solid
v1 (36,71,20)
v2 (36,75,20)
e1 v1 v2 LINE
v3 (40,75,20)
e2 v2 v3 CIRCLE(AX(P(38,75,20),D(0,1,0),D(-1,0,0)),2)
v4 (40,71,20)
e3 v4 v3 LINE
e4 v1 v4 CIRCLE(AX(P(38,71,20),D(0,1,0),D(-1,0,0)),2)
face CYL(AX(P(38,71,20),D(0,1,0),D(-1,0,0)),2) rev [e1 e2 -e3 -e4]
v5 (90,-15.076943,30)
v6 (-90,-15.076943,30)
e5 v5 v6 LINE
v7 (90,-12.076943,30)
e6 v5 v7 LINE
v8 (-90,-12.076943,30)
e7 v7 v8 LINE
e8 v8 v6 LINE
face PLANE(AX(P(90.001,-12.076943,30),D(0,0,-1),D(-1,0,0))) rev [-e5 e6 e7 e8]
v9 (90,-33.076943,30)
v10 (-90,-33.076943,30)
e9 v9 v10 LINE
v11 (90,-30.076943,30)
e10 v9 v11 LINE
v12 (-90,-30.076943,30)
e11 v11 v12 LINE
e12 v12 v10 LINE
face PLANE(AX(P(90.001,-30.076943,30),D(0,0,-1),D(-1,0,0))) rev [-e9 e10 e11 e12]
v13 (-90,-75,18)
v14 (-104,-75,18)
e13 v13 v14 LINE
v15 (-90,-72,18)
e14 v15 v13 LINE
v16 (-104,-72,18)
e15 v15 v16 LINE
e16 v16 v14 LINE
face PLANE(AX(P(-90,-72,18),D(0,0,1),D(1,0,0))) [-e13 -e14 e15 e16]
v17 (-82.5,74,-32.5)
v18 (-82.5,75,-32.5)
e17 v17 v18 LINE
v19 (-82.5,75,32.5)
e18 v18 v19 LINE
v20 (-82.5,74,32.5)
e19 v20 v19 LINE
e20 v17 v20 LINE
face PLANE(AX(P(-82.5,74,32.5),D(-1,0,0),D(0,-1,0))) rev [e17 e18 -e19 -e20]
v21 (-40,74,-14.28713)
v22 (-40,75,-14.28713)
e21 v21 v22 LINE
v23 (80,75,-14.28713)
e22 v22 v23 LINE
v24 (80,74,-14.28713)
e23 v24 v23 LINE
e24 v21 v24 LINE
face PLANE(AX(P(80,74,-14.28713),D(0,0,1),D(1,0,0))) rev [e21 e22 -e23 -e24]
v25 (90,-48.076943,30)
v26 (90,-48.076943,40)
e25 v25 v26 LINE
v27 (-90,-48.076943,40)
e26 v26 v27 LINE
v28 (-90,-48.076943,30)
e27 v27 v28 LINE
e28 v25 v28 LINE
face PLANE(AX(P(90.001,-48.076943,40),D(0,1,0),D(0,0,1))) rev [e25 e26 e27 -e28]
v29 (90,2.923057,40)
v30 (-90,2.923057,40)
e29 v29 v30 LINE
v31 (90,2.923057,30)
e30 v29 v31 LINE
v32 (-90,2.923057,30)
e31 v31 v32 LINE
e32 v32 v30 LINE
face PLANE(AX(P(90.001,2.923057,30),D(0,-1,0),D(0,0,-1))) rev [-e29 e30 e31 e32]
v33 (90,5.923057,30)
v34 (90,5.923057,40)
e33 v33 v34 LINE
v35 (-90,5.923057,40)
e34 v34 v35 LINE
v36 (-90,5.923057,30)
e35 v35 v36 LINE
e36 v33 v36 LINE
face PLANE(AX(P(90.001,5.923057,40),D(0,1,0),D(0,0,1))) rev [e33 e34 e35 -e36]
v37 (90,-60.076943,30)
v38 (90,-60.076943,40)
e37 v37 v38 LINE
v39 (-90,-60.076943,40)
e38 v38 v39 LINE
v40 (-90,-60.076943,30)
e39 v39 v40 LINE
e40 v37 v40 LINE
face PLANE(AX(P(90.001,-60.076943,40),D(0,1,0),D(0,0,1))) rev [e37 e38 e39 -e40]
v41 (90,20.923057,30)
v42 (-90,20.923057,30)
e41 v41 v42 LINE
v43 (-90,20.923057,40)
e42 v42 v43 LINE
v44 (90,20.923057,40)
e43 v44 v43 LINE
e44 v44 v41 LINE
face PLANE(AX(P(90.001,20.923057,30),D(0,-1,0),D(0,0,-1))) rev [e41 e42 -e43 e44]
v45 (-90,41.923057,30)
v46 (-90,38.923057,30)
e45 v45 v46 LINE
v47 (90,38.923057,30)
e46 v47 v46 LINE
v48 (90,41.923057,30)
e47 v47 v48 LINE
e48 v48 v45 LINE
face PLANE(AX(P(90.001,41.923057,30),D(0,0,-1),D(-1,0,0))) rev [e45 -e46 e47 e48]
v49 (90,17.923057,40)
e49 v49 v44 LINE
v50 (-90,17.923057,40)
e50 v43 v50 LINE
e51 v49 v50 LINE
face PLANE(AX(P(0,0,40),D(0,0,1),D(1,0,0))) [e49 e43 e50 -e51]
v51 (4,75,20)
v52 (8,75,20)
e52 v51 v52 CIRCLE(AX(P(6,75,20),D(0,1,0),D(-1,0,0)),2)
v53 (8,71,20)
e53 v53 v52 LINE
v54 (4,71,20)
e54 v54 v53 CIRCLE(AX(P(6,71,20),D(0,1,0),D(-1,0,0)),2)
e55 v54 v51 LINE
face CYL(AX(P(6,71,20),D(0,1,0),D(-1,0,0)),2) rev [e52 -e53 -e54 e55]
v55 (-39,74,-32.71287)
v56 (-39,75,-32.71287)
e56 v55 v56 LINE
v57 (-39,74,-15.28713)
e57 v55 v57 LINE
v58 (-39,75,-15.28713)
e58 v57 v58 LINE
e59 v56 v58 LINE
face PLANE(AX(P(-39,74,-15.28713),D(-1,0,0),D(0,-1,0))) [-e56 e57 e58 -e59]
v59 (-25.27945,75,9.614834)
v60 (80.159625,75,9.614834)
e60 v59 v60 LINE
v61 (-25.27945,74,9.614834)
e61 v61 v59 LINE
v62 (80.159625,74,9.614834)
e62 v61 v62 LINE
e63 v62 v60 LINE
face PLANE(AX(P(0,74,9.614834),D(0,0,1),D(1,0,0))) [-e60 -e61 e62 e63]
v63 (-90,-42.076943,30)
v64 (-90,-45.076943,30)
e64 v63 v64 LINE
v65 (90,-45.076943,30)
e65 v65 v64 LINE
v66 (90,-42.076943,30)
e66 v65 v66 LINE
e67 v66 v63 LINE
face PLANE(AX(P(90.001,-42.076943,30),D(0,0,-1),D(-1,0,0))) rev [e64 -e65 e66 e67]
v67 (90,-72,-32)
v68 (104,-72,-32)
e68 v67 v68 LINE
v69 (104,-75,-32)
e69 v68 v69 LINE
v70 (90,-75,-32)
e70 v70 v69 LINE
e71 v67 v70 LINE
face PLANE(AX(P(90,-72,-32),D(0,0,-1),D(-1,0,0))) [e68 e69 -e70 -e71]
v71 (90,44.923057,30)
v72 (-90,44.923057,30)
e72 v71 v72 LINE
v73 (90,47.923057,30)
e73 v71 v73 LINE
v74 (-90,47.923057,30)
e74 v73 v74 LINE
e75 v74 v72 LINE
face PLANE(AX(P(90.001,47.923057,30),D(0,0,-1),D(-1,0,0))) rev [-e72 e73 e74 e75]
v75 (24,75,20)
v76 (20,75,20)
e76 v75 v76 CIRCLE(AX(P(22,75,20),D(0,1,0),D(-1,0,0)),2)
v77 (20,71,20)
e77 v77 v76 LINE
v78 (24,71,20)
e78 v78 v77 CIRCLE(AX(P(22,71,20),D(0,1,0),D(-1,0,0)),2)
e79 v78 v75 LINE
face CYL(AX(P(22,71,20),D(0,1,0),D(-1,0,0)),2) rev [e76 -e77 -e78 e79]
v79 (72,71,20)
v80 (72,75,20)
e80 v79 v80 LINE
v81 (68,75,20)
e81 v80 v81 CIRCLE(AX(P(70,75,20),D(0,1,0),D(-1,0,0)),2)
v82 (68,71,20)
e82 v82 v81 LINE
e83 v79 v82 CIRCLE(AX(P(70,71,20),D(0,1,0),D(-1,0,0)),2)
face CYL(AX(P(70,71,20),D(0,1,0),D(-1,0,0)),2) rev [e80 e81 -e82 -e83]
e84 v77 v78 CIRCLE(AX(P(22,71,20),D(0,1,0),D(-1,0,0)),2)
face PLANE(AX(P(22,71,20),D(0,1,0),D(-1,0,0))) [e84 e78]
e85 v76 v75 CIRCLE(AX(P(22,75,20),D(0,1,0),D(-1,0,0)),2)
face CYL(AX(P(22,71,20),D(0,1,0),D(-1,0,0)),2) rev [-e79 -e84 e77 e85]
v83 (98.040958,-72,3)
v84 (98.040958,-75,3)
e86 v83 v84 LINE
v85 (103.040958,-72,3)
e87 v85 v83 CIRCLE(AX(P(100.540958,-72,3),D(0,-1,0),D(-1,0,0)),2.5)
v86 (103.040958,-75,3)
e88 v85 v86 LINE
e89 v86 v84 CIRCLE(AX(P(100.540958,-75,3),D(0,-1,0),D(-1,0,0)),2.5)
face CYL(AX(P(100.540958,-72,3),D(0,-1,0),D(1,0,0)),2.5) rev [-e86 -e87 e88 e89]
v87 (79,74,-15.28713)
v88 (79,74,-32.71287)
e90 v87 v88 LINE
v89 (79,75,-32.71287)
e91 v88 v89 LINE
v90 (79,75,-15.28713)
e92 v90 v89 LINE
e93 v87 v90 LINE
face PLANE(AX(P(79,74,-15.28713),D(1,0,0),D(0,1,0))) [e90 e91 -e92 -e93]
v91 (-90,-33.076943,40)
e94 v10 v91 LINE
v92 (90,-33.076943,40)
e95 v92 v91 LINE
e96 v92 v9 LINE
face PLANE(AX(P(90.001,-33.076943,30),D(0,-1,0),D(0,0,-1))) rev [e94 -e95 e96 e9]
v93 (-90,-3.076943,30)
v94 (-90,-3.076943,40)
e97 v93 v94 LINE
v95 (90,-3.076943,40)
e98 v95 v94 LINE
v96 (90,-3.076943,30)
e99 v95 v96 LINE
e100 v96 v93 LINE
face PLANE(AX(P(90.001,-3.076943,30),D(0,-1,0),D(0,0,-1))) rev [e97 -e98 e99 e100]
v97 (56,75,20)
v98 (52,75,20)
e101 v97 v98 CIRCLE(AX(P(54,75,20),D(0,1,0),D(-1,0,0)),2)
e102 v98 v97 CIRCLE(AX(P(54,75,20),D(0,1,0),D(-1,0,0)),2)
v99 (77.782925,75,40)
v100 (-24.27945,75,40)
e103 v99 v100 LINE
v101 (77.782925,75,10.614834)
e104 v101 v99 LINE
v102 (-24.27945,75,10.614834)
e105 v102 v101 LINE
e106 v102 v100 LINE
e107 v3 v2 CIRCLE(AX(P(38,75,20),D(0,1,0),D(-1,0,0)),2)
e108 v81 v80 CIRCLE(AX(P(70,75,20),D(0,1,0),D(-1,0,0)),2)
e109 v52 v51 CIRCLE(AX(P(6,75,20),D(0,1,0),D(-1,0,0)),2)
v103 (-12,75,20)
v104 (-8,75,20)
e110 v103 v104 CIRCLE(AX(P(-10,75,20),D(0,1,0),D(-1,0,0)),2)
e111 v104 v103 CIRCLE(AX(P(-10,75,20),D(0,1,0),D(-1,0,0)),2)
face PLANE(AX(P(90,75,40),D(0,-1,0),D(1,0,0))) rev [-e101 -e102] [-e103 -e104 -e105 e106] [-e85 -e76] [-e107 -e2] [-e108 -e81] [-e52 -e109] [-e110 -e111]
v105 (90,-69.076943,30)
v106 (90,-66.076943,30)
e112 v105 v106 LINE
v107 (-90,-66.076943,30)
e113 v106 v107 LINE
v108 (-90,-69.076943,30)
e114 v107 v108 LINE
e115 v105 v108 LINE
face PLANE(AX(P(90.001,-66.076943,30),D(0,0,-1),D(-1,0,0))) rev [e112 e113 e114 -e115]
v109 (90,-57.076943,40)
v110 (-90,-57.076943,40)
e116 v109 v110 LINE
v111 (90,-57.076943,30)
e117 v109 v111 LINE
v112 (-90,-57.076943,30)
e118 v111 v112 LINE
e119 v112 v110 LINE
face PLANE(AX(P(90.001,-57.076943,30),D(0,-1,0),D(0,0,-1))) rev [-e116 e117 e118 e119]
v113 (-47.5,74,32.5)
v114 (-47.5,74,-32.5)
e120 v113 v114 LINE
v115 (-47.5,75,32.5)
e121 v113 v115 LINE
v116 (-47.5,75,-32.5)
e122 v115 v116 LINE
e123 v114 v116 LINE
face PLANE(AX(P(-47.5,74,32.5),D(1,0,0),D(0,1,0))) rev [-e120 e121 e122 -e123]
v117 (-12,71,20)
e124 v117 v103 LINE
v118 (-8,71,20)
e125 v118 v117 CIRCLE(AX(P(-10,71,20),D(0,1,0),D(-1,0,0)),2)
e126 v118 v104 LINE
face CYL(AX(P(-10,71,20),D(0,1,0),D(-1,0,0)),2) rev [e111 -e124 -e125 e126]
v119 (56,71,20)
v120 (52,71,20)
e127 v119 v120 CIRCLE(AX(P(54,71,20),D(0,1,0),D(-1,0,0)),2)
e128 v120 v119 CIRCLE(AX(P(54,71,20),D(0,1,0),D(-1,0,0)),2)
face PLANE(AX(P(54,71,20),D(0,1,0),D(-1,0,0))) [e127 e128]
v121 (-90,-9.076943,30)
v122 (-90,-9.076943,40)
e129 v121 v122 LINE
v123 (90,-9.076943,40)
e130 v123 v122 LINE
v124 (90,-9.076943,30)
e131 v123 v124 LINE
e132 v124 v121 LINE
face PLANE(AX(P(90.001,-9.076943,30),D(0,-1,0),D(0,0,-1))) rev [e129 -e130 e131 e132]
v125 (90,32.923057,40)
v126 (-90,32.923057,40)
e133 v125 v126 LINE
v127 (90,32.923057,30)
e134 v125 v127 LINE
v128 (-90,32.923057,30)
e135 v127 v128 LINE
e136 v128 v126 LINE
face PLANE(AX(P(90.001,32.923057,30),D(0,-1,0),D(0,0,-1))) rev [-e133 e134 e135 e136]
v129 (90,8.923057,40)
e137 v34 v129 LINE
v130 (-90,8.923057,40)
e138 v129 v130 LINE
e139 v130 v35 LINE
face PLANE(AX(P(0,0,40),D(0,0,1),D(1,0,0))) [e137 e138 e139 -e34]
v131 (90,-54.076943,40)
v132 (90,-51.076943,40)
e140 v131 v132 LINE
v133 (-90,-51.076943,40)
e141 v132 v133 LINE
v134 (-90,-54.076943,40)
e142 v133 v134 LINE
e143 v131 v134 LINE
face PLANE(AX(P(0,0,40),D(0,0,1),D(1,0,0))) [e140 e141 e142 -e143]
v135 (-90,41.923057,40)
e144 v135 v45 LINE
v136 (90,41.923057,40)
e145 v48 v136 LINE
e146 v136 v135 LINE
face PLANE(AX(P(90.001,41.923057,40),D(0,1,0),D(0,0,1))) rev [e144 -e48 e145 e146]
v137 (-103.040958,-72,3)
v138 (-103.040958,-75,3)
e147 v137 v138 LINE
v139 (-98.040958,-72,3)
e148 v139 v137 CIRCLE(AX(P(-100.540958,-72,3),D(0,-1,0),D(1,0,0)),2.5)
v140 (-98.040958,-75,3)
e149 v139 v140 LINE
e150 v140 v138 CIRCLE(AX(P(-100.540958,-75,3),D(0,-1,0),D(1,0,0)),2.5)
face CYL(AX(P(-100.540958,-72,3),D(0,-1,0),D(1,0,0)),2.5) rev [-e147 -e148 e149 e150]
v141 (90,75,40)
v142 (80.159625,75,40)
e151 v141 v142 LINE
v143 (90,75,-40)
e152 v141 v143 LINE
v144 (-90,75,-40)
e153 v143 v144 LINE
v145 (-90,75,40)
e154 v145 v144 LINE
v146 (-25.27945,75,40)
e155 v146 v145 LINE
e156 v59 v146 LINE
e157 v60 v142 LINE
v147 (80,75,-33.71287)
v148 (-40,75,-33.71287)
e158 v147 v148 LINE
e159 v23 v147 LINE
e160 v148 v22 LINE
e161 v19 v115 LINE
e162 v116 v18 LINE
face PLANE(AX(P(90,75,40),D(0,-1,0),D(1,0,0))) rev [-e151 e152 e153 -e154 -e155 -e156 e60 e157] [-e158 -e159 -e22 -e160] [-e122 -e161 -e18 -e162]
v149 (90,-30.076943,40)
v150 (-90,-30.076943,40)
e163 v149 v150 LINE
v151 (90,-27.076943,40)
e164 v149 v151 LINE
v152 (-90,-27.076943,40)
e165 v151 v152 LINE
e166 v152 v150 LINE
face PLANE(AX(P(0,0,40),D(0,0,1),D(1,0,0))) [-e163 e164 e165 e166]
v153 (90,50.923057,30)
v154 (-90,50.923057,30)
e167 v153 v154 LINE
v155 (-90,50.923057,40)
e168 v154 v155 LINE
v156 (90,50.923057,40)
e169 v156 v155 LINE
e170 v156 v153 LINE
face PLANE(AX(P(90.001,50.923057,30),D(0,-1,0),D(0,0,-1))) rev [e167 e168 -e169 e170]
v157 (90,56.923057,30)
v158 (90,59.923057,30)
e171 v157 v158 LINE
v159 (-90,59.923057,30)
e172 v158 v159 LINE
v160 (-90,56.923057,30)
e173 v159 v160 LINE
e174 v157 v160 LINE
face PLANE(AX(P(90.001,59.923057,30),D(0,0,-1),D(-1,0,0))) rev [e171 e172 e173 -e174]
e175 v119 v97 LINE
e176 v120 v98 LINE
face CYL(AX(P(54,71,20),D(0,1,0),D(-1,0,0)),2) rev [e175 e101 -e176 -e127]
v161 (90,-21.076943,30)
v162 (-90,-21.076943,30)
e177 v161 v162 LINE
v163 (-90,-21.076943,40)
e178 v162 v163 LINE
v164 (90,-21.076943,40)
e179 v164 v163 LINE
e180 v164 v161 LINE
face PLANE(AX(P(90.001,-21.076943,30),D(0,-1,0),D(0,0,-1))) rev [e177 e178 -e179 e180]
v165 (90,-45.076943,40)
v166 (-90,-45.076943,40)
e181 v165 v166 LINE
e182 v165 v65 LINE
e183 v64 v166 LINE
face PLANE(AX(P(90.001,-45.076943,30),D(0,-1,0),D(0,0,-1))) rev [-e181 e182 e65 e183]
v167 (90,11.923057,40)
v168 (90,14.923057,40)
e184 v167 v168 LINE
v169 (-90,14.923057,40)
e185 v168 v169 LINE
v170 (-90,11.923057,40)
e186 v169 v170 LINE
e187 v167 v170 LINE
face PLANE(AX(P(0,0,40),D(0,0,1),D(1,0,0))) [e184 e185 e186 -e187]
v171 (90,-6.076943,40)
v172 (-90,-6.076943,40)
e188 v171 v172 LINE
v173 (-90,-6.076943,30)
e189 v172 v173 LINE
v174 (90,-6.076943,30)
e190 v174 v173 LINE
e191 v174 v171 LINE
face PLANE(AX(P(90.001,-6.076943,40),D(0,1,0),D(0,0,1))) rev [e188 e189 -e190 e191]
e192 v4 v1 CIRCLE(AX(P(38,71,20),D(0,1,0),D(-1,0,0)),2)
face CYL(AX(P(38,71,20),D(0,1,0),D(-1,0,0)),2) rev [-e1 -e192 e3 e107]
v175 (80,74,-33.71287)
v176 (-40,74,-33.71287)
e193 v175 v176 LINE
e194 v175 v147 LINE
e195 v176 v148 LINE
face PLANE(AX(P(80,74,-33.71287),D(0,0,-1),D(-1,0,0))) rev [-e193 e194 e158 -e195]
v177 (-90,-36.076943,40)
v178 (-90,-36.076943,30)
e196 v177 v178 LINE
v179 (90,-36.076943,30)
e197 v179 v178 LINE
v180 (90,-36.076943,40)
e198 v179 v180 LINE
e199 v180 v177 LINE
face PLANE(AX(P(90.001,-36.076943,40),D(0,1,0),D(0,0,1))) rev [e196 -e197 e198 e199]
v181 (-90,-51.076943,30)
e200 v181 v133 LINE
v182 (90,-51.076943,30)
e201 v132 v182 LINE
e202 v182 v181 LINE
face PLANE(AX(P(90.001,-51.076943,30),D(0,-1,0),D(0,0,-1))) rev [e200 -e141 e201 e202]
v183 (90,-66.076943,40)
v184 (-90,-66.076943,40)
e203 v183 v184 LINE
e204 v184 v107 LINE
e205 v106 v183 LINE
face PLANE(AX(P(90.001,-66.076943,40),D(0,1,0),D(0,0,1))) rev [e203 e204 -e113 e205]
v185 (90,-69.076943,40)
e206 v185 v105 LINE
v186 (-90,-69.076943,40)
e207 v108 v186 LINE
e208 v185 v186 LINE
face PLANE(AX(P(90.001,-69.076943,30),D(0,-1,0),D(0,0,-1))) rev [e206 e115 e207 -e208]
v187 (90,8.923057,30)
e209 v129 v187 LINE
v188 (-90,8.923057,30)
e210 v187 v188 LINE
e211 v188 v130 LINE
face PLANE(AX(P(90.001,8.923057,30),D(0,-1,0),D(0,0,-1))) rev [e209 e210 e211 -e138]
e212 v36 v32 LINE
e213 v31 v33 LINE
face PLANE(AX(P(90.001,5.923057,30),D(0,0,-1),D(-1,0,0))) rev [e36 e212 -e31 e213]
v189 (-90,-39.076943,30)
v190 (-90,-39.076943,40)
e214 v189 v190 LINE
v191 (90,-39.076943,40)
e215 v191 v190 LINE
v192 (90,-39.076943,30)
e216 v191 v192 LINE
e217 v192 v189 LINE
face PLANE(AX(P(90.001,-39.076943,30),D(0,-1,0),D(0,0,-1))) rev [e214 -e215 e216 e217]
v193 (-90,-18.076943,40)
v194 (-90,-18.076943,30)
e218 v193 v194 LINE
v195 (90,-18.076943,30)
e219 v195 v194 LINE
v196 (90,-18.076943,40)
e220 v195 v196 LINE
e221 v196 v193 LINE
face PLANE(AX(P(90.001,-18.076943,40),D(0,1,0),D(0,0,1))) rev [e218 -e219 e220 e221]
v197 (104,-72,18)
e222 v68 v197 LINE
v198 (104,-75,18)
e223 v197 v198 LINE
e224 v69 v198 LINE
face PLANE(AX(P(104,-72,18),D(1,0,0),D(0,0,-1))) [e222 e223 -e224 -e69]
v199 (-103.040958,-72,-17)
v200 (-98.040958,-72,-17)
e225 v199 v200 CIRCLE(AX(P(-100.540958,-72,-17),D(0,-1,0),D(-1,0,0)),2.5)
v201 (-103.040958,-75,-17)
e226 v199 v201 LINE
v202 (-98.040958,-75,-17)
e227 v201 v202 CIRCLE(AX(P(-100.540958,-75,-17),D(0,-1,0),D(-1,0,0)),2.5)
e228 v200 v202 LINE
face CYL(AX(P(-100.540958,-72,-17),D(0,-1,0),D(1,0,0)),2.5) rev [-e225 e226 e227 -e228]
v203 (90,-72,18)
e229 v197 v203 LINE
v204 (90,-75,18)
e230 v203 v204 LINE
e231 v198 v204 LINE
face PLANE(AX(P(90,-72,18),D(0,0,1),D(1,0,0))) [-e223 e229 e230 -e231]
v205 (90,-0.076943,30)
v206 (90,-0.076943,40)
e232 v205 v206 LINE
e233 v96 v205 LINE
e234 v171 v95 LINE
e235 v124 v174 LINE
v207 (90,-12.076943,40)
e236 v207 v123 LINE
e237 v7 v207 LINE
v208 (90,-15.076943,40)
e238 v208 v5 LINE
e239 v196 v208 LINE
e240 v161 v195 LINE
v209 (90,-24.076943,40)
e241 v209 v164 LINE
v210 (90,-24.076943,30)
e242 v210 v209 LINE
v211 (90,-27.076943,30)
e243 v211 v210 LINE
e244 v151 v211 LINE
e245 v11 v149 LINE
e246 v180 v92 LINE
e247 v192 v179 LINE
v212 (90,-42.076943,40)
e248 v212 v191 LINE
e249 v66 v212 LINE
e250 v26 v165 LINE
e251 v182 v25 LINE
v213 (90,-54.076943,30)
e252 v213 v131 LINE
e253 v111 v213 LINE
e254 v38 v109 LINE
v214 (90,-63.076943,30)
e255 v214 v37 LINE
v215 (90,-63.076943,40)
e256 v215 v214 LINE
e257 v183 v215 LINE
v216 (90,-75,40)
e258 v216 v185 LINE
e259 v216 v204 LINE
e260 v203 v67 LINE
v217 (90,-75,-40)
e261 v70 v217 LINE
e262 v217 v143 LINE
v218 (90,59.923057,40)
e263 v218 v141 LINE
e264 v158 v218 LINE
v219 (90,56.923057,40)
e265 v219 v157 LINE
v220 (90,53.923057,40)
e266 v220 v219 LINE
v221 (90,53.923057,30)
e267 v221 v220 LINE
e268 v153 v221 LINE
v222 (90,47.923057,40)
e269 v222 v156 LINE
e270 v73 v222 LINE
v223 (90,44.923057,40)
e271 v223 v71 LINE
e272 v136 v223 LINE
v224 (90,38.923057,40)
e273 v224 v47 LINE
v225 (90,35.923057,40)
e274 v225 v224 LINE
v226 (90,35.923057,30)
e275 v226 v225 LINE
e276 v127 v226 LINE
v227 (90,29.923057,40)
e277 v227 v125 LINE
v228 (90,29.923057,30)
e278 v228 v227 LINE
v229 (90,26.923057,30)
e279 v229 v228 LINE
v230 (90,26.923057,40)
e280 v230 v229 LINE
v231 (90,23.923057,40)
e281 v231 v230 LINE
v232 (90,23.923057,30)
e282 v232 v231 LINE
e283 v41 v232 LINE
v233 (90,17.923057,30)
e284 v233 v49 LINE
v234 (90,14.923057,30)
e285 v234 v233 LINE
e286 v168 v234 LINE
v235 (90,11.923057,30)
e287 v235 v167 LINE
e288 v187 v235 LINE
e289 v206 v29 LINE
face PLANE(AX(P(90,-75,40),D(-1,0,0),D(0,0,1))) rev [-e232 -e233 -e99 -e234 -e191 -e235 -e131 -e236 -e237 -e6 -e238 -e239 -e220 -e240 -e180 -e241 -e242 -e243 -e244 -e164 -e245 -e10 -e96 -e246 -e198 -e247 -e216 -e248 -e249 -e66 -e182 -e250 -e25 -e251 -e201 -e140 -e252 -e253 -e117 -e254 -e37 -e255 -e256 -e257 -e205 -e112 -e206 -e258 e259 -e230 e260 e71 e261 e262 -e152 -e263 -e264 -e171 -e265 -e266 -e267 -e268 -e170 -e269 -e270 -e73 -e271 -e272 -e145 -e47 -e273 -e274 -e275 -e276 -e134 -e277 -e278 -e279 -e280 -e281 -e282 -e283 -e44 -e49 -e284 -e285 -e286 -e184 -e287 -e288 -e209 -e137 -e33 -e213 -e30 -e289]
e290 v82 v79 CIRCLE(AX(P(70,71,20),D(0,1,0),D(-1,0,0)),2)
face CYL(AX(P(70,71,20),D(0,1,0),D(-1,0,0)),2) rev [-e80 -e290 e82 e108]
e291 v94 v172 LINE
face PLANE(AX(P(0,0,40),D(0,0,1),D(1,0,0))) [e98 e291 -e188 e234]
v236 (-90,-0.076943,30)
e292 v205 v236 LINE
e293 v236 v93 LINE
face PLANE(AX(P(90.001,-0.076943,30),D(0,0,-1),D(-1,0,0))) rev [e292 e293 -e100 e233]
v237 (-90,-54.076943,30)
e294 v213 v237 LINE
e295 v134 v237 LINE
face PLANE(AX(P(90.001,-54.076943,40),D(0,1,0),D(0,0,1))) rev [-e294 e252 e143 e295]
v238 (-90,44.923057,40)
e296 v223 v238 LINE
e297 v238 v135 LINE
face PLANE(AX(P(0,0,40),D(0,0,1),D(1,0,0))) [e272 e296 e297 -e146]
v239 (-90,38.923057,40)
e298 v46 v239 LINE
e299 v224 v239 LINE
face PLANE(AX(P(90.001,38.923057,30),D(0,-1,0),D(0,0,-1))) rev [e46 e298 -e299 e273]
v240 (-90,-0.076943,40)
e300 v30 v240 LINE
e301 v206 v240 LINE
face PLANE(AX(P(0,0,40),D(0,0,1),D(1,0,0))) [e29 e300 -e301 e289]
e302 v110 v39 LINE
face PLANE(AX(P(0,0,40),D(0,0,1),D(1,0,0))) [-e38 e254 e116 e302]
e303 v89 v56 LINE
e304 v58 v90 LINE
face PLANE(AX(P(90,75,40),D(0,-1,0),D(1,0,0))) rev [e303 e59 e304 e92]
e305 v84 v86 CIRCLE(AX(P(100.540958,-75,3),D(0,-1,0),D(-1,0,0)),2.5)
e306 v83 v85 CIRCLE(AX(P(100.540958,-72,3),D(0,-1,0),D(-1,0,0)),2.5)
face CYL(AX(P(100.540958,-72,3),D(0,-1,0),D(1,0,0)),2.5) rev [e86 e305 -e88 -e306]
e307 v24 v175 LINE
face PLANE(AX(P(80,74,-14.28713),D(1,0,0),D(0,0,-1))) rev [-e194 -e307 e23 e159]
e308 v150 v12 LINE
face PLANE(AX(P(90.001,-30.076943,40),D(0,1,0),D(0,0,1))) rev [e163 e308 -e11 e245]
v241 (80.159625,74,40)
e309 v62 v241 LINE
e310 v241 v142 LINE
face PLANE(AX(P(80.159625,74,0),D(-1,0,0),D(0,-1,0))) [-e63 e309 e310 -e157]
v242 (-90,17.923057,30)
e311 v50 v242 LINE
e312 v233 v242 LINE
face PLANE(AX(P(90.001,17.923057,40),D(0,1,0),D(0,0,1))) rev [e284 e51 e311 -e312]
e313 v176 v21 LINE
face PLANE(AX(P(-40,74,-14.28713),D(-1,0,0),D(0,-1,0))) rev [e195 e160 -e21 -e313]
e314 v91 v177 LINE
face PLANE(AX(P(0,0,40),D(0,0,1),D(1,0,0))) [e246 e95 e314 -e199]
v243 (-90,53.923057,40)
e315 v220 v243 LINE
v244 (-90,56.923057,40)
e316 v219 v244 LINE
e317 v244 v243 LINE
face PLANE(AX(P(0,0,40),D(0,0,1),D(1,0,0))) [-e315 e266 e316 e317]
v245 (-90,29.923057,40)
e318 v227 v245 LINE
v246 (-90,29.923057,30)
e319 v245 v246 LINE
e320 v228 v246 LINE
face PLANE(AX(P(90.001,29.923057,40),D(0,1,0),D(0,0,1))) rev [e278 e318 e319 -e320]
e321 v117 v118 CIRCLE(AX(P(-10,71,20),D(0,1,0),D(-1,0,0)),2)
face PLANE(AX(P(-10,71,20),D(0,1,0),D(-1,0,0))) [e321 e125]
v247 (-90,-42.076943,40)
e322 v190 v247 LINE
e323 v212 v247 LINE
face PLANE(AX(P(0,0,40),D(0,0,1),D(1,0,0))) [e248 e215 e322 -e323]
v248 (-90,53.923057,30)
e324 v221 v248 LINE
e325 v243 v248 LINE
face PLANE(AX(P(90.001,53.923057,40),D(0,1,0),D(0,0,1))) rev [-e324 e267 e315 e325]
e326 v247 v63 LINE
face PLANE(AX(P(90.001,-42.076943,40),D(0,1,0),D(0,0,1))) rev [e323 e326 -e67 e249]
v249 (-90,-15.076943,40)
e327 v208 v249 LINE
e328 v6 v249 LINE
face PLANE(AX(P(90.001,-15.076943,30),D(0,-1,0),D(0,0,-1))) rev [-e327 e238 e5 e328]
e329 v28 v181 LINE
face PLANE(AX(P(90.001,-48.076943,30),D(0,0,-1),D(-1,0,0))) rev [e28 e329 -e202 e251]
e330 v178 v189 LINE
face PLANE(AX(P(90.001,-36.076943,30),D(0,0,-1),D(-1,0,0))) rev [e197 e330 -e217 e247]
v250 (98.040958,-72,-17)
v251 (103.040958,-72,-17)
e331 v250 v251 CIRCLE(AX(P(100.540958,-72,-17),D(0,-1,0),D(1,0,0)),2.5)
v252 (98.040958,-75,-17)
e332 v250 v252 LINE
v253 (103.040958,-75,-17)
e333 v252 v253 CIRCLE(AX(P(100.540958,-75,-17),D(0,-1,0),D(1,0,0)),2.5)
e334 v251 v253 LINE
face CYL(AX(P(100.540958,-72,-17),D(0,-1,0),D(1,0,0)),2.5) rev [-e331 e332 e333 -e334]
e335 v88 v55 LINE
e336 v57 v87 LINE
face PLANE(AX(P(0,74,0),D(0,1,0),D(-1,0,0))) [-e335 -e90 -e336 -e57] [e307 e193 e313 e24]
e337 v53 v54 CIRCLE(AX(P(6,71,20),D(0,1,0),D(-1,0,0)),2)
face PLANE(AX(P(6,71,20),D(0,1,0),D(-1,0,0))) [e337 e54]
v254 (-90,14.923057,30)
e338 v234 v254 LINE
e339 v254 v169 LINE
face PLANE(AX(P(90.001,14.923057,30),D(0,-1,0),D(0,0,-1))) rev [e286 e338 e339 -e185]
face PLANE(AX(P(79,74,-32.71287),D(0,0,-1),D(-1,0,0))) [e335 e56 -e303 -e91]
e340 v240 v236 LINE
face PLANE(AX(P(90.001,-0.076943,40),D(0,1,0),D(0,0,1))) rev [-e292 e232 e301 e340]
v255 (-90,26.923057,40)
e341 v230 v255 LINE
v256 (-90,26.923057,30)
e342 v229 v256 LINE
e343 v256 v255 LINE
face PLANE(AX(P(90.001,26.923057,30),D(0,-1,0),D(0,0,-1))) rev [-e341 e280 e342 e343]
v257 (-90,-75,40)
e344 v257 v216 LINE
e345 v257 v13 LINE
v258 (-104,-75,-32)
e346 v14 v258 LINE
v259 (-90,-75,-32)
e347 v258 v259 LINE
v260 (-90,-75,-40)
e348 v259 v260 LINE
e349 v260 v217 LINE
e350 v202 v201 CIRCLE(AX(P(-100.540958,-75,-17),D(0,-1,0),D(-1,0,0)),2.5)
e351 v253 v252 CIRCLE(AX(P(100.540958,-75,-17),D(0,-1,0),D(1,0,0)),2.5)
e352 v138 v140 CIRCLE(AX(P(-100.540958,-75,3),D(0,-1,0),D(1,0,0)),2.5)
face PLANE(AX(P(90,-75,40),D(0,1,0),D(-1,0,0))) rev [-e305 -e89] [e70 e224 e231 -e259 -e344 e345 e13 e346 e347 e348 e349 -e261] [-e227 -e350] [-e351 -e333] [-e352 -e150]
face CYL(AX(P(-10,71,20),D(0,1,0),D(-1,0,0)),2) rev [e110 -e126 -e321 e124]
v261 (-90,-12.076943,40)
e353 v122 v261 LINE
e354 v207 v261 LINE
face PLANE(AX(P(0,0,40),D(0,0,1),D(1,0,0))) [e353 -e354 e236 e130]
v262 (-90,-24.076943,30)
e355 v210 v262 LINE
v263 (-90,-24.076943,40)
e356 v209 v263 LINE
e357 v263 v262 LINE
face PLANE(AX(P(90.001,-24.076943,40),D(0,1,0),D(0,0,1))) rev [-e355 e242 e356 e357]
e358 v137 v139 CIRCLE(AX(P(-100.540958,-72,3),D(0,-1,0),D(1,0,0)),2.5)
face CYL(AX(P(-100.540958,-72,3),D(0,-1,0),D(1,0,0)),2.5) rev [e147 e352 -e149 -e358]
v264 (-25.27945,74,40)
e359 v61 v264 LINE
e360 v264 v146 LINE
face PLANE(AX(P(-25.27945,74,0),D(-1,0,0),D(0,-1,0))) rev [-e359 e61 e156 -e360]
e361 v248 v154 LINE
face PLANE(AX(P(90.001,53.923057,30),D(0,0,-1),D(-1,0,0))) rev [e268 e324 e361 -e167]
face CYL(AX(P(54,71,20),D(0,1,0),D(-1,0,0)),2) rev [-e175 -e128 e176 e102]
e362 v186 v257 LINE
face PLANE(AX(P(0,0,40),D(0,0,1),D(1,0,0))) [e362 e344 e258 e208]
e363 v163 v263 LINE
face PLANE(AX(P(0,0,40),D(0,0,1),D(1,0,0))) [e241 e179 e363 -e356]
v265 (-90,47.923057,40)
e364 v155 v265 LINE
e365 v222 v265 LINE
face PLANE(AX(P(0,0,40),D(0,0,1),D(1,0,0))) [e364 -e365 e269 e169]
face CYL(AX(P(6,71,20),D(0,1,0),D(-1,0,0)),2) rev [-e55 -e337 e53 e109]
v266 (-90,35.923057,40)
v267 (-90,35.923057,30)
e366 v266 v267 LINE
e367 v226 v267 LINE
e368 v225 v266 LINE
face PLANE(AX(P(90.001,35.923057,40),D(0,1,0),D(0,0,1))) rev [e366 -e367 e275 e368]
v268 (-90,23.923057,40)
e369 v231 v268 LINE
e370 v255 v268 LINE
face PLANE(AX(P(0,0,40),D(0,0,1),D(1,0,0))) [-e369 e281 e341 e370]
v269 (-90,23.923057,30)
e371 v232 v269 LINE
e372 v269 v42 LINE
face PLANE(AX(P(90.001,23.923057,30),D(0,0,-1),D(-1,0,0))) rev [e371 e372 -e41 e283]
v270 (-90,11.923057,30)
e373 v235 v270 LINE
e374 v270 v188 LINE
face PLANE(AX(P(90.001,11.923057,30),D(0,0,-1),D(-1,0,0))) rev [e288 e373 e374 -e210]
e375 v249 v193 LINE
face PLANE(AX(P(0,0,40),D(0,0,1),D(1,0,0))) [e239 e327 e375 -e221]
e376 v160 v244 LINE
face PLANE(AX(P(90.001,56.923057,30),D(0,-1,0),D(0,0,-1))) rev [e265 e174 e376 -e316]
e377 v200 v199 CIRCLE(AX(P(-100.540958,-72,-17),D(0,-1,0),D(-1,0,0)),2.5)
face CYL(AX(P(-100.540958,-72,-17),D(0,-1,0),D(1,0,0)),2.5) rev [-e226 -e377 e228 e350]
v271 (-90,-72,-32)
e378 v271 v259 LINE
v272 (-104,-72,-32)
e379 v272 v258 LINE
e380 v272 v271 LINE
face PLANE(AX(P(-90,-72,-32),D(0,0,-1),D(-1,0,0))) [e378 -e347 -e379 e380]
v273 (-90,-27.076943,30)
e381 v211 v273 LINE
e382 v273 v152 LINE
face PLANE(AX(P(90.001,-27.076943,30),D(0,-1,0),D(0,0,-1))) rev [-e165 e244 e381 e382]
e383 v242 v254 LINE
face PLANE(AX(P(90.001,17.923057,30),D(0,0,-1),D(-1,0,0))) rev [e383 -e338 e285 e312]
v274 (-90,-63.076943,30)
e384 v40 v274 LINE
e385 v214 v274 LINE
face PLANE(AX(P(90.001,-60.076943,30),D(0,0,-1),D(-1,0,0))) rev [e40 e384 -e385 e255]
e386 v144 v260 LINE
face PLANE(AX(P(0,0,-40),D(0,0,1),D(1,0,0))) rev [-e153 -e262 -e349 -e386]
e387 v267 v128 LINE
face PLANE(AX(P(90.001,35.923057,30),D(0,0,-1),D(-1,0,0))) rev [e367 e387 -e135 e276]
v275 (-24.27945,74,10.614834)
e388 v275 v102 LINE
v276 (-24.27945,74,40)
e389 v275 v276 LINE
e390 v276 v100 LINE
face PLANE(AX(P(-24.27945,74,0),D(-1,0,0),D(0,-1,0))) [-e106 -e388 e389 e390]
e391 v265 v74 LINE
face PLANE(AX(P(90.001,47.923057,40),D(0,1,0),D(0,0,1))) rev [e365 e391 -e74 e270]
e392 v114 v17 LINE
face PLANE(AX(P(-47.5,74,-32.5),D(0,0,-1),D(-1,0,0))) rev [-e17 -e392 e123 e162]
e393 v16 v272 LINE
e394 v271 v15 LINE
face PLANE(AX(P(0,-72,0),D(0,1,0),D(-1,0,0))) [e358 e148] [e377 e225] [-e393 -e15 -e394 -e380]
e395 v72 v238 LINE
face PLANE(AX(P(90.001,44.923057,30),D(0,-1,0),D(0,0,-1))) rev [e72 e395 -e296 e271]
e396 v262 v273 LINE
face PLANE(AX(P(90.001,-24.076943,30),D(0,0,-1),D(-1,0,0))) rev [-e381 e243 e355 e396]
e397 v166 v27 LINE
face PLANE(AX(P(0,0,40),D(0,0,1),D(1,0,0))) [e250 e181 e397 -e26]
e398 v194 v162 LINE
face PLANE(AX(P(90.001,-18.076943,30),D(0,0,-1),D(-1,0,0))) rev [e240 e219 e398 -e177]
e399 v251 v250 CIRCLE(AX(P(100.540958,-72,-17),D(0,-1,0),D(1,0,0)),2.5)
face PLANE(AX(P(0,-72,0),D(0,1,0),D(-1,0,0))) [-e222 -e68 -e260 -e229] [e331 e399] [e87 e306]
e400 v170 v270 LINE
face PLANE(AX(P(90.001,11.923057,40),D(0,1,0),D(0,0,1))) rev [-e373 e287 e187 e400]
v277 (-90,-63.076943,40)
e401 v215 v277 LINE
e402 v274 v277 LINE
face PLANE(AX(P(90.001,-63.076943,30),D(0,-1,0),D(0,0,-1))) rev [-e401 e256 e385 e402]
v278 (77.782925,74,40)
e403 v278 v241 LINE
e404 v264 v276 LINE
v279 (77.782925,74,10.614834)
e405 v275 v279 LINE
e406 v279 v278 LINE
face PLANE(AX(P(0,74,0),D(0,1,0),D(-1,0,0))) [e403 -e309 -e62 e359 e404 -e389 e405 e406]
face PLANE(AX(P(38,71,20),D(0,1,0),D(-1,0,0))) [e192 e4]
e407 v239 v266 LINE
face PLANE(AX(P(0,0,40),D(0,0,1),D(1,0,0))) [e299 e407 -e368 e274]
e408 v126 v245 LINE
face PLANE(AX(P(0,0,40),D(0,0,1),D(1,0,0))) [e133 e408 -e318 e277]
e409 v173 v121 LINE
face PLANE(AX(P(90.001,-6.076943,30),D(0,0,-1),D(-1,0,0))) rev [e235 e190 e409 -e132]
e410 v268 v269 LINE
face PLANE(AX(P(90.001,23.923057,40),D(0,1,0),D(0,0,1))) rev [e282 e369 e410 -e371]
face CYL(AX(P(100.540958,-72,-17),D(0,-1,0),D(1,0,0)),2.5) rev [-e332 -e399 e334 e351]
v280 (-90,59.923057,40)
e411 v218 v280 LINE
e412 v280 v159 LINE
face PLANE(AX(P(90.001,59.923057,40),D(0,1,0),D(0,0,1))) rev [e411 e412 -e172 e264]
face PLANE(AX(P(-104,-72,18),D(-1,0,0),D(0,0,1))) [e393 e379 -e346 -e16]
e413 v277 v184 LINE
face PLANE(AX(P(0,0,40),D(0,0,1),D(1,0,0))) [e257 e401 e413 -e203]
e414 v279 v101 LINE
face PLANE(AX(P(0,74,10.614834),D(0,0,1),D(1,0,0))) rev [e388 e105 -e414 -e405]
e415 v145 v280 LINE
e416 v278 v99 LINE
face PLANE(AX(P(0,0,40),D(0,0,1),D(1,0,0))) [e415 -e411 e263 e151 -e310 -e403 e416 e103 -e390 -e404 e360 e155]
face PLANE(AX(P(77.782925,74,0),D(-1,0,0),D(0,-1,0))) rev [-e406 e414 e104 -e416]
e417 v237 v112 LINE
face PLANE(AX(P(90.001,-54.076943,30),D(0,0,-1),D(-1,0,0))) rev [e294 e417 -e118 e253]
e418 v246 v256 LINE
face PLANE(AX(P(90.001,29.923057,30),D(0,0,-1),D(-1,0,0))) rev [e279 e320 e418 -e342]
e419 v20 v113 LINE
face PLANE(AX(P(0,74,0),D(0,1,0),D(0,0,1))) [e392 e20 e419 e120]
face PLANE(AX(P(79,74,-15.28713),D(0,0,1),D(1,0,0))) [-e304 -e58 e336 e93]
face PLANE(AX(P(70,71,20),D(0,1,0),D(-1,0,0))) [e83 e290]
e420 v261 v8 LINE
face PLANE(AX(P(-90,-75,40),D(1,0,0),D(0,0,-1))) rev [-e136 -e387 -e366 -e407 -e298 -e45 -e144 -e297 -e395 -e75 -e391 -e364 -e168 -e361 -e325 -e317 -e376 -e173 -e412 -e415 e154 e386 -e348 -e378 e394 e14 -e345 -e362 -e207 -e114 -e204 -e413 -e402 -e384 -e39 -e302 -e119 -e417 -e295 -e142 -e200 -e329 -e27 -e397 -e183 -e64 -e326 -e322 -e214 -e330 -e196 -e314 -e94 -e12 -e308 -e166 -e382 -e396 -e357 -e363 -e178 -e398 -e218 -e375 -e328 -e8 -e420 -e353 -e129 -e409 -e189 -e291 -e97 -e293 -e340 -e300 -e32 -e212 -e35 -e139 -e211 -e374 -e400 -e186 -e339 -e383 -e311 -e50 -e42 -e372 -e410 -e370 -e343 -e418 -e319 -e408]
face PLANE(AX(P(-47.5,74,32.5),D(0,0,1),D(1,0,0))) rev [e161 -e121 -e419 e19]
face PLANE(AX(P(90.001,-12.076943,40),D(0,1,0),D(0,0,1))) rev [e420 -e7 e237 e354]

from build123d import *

# Parameters (mm, degrees)
SKETCH_1_W          = 180
SKETCH_1_H          = 150
EXTRUDE_1_DEPTH     = 40
CUT_EXTRUDE_1_REACH = 201.06
SKETCH_2_W          = 10
SKETCH_2_H          = 3
SKETCH_3_W          = 35
SKETCH_3_H          = 65
CUT_EXTRUDE_2_DEPTH = 1
SKETCH_4_W          = 120
SKETCH_4_H          = 19.42574098
SKETCH_4_W_2        = 118
SKETCH_4_H_2        = 17.42574098
CUT_EXTRUDE_3_DEPTH = 1
SKETCH_5_W          = 14
SKETCH_5_H          = 50
SKETCH_5_R          = 2.5
EXTRUDE_2_DEPTH     = 3
SKETCH_6_R          = 2
CUT_EXTRUDE_4_DEPTH = 4
CUT_EXTRUDE_5_DEPTH = 1


with BuildPart() as part:
    # 草图1 → 凸台-拉伸1 (new, symmetric)
    with BuildSketch(Plane.XY):
        Rectangle(SKETCH_1_W, SKETCH_1_H)
    extrude(amount=EXTRUDE_1_DEPTH, both=True)

    # 草图2 → 切除-拉伸1 (cut, up to next)
    with BuildSketch(Plane.ZY.offset(90), mode=Mode.PRIVATE) as cut_extrude_1_sk1:
        with Locations((35, 58.423056781)):
            Rectangle(SKETCH_2_W, SKETCH_2_H)
    cut_extrude_1_tool1 = extrude(cut_extrude_1_sk1.sketch, amount=-CUT_EXTRUDE_1_REACH, mode=Mode.PRIVATE) & part.part
    # 草图2 → 切除-拉伸1 (cut, up to next)
    with BuildSketch(Plane.ZY.offset(90), mode=Mode.PRIVATE) as cut_extrude_1_sk2:
        with Locations((35, 52.423056781)):
            Rectangle(SKETCH_2_W, SKETCH_2_H)
    cut_extrude_1_tool2 = extrude(cut_extrude_1_sk2.sketch, amount=-CUT_EXTRUDE_1_REACH, mode=Mode.PRIVATE) & part.part
    # 草图2 → 切除-拉伸1 (cut, up to next)
    with BuildSketch(Plane.ZY.offset(90), mode=Mode.PRIVATE) as cut_extrude_1_sk3:
        with Locations((35, 46.423056781)):
            Rectangle(SKETCH_2_W, SKETCH_2_H)
    cut_extrude_1_tool3 = extrude(cut_extrude_1_sk3.sketch, amount=-CUT_EXTRUDE_1_REACH, mode=Mode.PRIVATE) & part.part
    # 草图2 → 切除-拉伸1 (cut, up to next)
    with BuildSketch(Plane.ZY.offset(90), mode=Mode.PRIVATE) as cut_extrude_1_sk4:
        with Locations((35, 40.423056781)):
            Rectangle(SKETCH_2_W, SKETCH_2_H)
    cut_extrude_1_tool4 = extrude(cut_extrude_1_sk4.sketch, amount=-CUT_EXTRUDE_1_REACH, mode=Mode.PRIVATE) & part.part
    # 草图2 → 切除-拉伸1 (cut, up to next)
    with BuildSketch(Plane.ZY.offset(90), mode=Mode.PRIVATE) as cut_extrude_1_sk5:
        with Locations((35, 34.423056781)):
            Rectangle(SKETCH_2_W, SKETCH_2_H)
    cut_extrude_1_tool5 = extrude(cut_extrude_1_sk5.sketch, amount=-CUT_EXTRUDE_1_REACH, mode=Mode.PRIVATE) & part.part
    # 草图2 → 切除-拉伸1 (cut, up to next)
    with BuildSketch(Plane.ZY.offset(90), mode=Mode.PRIVATE) as cut_extrude_1_sk6:
        with Locations((35, 28.423056781)):
            Rectangle(SKETCH_2_W, SKETCH_2_H)
    cut_extrude_1_tool6 = extrude(cut_extrude_1_sk6.sketch, amount=-CUT_EXTRUDE_1_REACH, mode=Mode.PRIVATE) & part.part
    # 草图2 → 切除-拉伸1 (cut, up to next)
    with BuildSketch(Plane.ZY.offset(90), mode=Mode.PRIVATE) as cut_extrude_1_sk7:
        with Locations((35, 22.423056781)):
            Rectangle(SKETCH_2_W, SKETCH_2_H)
    cut_extrude_1_tool7 = extrude(cut_extrude_1_sk7.sketch, amount=-CUT_EXTRUDE_1_REACH, mode=Mode.PRIVATE) & part.part
    # 草图2 → 切除-拉伸1 (cut, up to next)
    with BuildSketch(Plane.ZY.offset(90), mode=Mode.PRIVATE) as cut_extrude_1_sk8:
        with Locations((35, 16.423056781)):
            Rectangle(SKETCH_2_W, SKETCH_2_H)
    cut_extrude_1_tool8 = extrude(cut_extrude_1_sk8.sketch, amount=-CUT_EXTRUDE_1_REACH, mode=Mode.PRIVATE) & part.part
    # 草图2 → 切除-拉伸1 (cut, up to next)
    with BuildSketch(Plane.ZY.offset(90), mode=Mode.PRIVATE) as cut_extrude_1_sk9:
        with Locations((35, 10.423056781)):
            Rectangle(SKETCH_2_W, SKETCH_2_H)
    cut_extrude_1_tool9 = extrude(cut_extrude_1_sk9.sketch, amount=-CUT_EXTRUDE_1_REACH, mode=Mode.PRIVATE) & part.part
    # 草图2 → 切除-拉伸1 (cut, up to next)
    with BuildSketch(Plane.ZY.offset(90), mode=Mode.PRIVATE) as cut_extrude_1_sk10:
        with Locations((35, 4.423056781)):
            Rectangle(SKETCH_2_W, SKETCH_2_H)
    cut_extrude_1_tool10 = extrude(cut_extrude_1_sk10.sketch, amount=-CUT_EXTRUDE_1_REACH, mode=Mode.PRIVATE) & part.part
    # 草图2 → 切除-拉伸1 (cut, up to next)
    with BuildSketch(Plane.ZY.offset(90), mode=Mode.PRIVATE) as cut_extrude_1_sk11:
        with Locations((35, -1.576943219)):
            Rectangle(SKETCH_2_W, SKETCH_2_H)
    cut_extrude_1_tool11 = extrude(cut_extrude_1_sk11.sketch, amount=-CUT_EXTRUDE_1_REACH, mode=Mode.PRIVATE) & part.part
    # 草图2 → 切除-拉伸1 (cut, up to next)
    with BuildSketch(Plane.ZY.offset(90), mode=Mode.PRIVATE) as cut_extrude_1_sk12:
        with Locations((35, -7.576943219)):
            Rectangle(SKETCH_2_W, SKETCH_2_H)
    cut_extrude_1_tool12 = extrude(cut_extrude_1_sk12.sketch, amount=-CUT_EXTRUDE_1_REACH, mode=Mode.PRIVATE) & part.part
    # 草图2 → 切除-拉伸1 (cut, up to next)
    with BuildSketch(Plane.ZY.offset(90), mode=Mode.PRIVATE) as cut_extrude_1_sk13:
        with Locations((35, -13.576943219)):
            Rectangle(SKETCH_2_W, SKETCH_2_H)
    cut_extrude_1_tool13 = extrude(cut_extrude_1_sk13.sketch, amount=-CUT_EXTRUDE_1_REACH, mode=Mode.PRIVATE) & part.part
    # 草图2 → 切除-拉伸1 (cut, up to next)
    with BuildSketch(Plane.ZY.offset(90), mode=Mode.PRIVATE) as cut_extrude_1_sk14:
        with Locations((35, -19.576943219)):
            Rectangle(SKETCH_2_W, SKETCH_2_H)
    cut_extrude_1_tool14 = extrude(cut_extrude_1_sk14.sketch, amount=-CUT_EXTRUDE_1_REACH, mode=Mode.PRIVATE) & part.part
    # 草图2 → 切除-拉伸1 (cut, up to next)
    with BuildSketch(Plane.ZY.offset(90), mode=Mode.PRIVATE) as cut_extrude_1_sk15:
        with Locations((35, -25.576943219)):
            Rectangle(SKETCH_2_W, SKETCH_2_H)
    cut_extrude_1_tool15 = extrude(cut_extrude_1_sk15.sketch, amount=-CUT_EXTRUDE_1_REACH, mode=Mode.PRIVATE) & part.part
    # 草图2 → 切除-拉伸1 (cut, up to next)
    with BuildSketch(Plane.ZY.offset(90), mode=Mode.PRIVATE) as cut_extrude_1_sk16:
        with Locations((35, -31.576943219)):
            Rectangle(SKETCH_2_W, SKETCH_2_H)
    cut_extrude_1_tool16 = extrude(cut_extrude_1_sk16.sketch, amount=-CUT_EXTRUDE_1_REACH, mode=Mode.PRIVATE) & part.part
    # 草图2 → 切除-拉伸1 (cut, up to next)
    with BuildSketch(Plane.ZY.offset(90), mode=Mode.PRIVATE) as cut_extrude_1_sk17:
        with Locations((35, -37.576943219)):
            Rectangle(SKETCH_2_W, SKETCH_2_H)
    cut_extrude_1_tool17 = extrude(cut_extrude_1_sk17.sketch, amount=-CUT_EXTRUDE_1_REACH, mode=Mode.PRIVATE) & part.part
    # 草图2 → 切除-拉伸1 (cut, up to next)
    with BuildSketch(Plane.ZY.offset(90), mode=Mode.PRIVATE) as cut_extrude_1_sk18:
        with Locations((35, -43.576943219)):
            Rectangle(SKETCH_2_W, SKETCH_2_H)
    cut_extrude_1_tool18 = extrude(cut_extrude_1_sk18.sketch, amount=-CUT_EXTRUDE_1_REACH, mode=Mode.PRIVATE) & part.part
    # 草图2 → 切除-拉伸1 (cut, up to next)
    with BuildSketch(Plane.ZY.offset(90), mode=Mode.PRIVATE) as cut_extrude_1_sk19:
        with Locations((35, -49.576943219)):
            Rectangle(SKETCH_2_W, SKETCH_2_H)
    cut_extrude_1_tool19 = extrude(cut_extrude_1_sk19.sketch, amount=-CUT_EXTRUDE_1_REACH, mode=Mode.PRIVATE) & part.part
    # 草图2 → 切除-拉伸1 (cut, up to next)
    with BuildSketch(Plane.ZY.offset(90), mode=Mode.PRIVATE) as cut_extrude_1_sk20:
        with Locations((35, -55.576943219)):
            Rectangle(SKETCH_2_W, SKETCH_2_H)
    cut_extrude_1_tool20 = extrude(cut_extrude_1_sk20.sketch, amount=-CUT_EXTRUDE_1_REACH, mode=Mode.PRIVATE) & part.part
    # 草图2 → 切除-拉伸1 (cut, up to next)
    with BuildSketch(Plane.ZY.offset(90), mode=Mode.PRIVATE) as cut_extrude_1_sk21:
        with Locations((35, -61.576943219)):
            Rectangle(SKETCH_2_W, SKETCH_2_H)
    cut_extrude_1_tool21 = extrude(cut_extrude_1_sk21.sketch, amount=-CUT_EXTRUDE_1_REACH, mode=Mode.PRIVATE) & part.part
    # 草图2 → 切除-拉伸1 (cut, up to next)
    with BuildSketch(Plane.ZY.offset(90), mode=Mode.PRIVATE) as cut_extrude_1_sk22:
        with Locations((35, -67.576943219)):
            Rectangle(SKETCH_2_W, SKETCH_2_H)
    cut_extrude_1_tool22 = extrude(cut_extrude_1_sk22.sketch, amount=-CUT_EXTRUDE_1_REACH, mode=Mode.PRIVATE) & part.part
    add(cut_extrude_1_tool1.solids().sort_by_distance((-90, 58.423057, 35))[0], mode=Mode.SUBTRACT)
    add(cut_extrude_1_tool2.solids().sort_by_distance((-90, 52.423057, 35))[0], mode=Mode.SUBTRACT)
    add(cut_extrude_1_tool3.solids().sort_by_distance((-90, 46.423057, 35))[0], mode=Mode.SUBTRACT)
    add(cut_extrude_1_tool4.solids().sort_by_distance((-90, 40.423057, 35))[0], mode=Mode.SUBTRACT)
    add(cut_extrude_1_tool5.solids().sort_by_distance((-90, 34.423057, 35))[0], mode=Mode.SUBTRACT)
    add(cut_extrude_1_tool6.solids().sort_by_distance((-90, 28.423057, 35))[0], mode=Mode.SUBTRACT)
    add(cut_extrude_1_tool7.solids().sort_by_distance((-90, 22.423057, 35))[0], mode=Mode.SUBTRACT)
    add(cut_extrude_1_tool8.solids().sort_by_distance((-90, 16.423057, 35))[0], mode=Mode.SUBTRACT)
    add(cut_extrude_1_tool9.solids().sort_by_distance((-90, 10.423057, 35))[0], mode=Mode.SUBTRACT)
    add(cut_extrude_1_tool10.solids().sort_by_distance((-90, 4.423057, 35))[0], mode=Mode.SUBTRACT)
    add(cut_extrude_1_tool11.solids().sort_by_distance((-90, -1.576943, 35))[0], mode=Mode.SUBTRACT)
    add(cut_extrude_1_tool12.solids().sort_by_distance((-90, -7.576943, 35))[0], mode=Mode.SUBTRACT)
    add(cut_extrude_1_tool13.solids().sort_by_distance((-90, -13.576943, 35))[0], mode=Mode.SUBTRACT)
    add(cut_extrude_1_tool14.solids().sort_by_distance((-90, -19.576943, 35))[0], mode=Mode.SUBTRACT)
    add(cut_extrude_1_tool15.solids().sort_by_distance((-90, -25.576943, 35))[0], mode=Mode.SUBTRACT)
    add(cut_extrude_1_tool16.solids().sort_by_distance((-90, -31.576943, 35))[0], mode=Mode.SUBTRACT)
    add(cut_extrude_1_tool17.solids().sort_by_distance((-90, -37.576943, 35))[0], mode=Mode.SUBTRACT)
    add(cut_extrude_1_tool18.solids().sort_by_distance((-90, -43.576943, 35))[0], mode=Mode.SUBTRACT)
    add(cut_extrude_1_tool19.solids().sort_by_distance((-90, -49.576943, 35))[0], mode=Mode.SUBTRACT)
    add(cut_extrude_1_tool20.solids().sort_by_distance((-90, -55.576943, 35))[0], mode=Mode.SUBTRACT)
    add(cut_extrude_1_tool21.solids().sort_by_distance((-90, -61.576943, 35))[0], mode=Mode.SUBTRACT)
    add(cut_extrude_1_tool22.solids().sort_by_distance((-90, -67.576943, 35))[0], mode=Mode.SUBTRACT)

    # 草图3 → 切除-拉伸2 (cut)
    with BuildSketch(Plane(origin=(0, 75, 0), x_dir=(1, 0, 0), z_dir=(0, 1, 0))):
        with Locations((-65, 0)):
            Rectangle(SKETCH_3_W, SKETCH_3_H)
    extrude(amount=-CUT_EXTRUDE_2_DEPTH, mode=Mode.SUBTRACT)

    # 草图4 → 切除-拉伸3 (cut)
    with BuildSketch(Plane(origin=(0, 75, 0), x_dir=(1, 0, 0), z_dir=(0, 1, 0))):
        with Locations((20, 24)):
            Rectangle(SKETCH_4_W, SKETCH_4_H)
        with Locations((20, 24)):
            Rectangle(SKETCH_4_W_2, SKETCH_4_H_2, mode=Mode.SUBTRACT)
    extrude(amount=-CUT_EXTRUDE_3_DEPTH, mode=Mode.SUBTRACT)

    # 草图5 → 凸台-拉伸2 (add)
    # profile 1 of 2: a face of its own
    with BuildSketch(Plane.XZ.offset(75)):
        with Locations((-97, -7)):
            Rectangle(SKETCH_5_W, SKETCH_5_H)
        with Locations((-100.540957797, 3)):
            Circle(SKETCH_5_R, mode=Mode.SUBTRACT)
        with Locations(Location((-100.540957797, -17, 0), (0, 0, 180))):
            Circle(SKETCH_5_R, mode=Mode.SUBTRACT)
    # profile 2 of 2: a face of its own
    with BuildSketch(Plane.XZ.offset(75)):
        with Locations((97, -7)):
            Rectangle(SKETCH_5_W, SKETCH_5_H)
        with Locations(Location((100.540957797, 3, 0), (0, 0, 180))):
            Circle(SKETCH_5_R, mode=Mode.SUBTRACT)
        with Locations((100.540957797, -17)):
            Circle(SKETCH_5_R, mode=Mode.SUBTRACT)
    extrude(amount=-EXTRUDE_2_DEPTH)

    # 草图6 → 切除-拉伸4 (cut)
    with BuildSketch(Plane(origin=(0, 75, 0), x_dir=(1, 0, 0), z_dir=(0, 1, 0))):
        with Locations(Location((-10, -20, 0), (0, 0, 180))):
            Circle(SKETCH_6_R)
        with Locations(Location((6, -20, 0), (0, 0, 180))):
            Circle(SKETCH_6_R)
        with Locations(Location((22, -20, 0), (0, 0, 180))):
            Circle(SKETCH_6_R)
        with Locations(Location((38, -20, 0), (0, 0, 180))):
            Circle(SKETCH_6_R)
        with Locations(Location((54, -20, 0), (0, 0, 180))):
            Circle(SKETCH_6_R)
        with Locations(Location((70, -20, 0), (0, 0, 180))):
            Circle(SKETCH_6_R)
    extrude(amount=-CUT_EXTRUDE_4_DEPTH, mode=Mode.SUBTRACT)

    # 草图7 → 切除-拉伸5 (cut)
    with BuildSketch(Plane(origin=(0, 75, 0), x_dir=(1, 0, 0), z_dir=(0, 1, 0))):
        Polygon((80.159624987, -9.614833725), (-25.279450467, -9.614833725), (-25.279450467, -40), (-24.279450467, -40), (-24.279450467, -10.614833725), (77.782924515, -10.614833725), (77.782924515, -40), (80.159624987, -40), align=None)
    extrude(amount=-CUT_EXTRUDE_5_DEPTH, mode=Mode.SUBTRACT)


solid = part.part
